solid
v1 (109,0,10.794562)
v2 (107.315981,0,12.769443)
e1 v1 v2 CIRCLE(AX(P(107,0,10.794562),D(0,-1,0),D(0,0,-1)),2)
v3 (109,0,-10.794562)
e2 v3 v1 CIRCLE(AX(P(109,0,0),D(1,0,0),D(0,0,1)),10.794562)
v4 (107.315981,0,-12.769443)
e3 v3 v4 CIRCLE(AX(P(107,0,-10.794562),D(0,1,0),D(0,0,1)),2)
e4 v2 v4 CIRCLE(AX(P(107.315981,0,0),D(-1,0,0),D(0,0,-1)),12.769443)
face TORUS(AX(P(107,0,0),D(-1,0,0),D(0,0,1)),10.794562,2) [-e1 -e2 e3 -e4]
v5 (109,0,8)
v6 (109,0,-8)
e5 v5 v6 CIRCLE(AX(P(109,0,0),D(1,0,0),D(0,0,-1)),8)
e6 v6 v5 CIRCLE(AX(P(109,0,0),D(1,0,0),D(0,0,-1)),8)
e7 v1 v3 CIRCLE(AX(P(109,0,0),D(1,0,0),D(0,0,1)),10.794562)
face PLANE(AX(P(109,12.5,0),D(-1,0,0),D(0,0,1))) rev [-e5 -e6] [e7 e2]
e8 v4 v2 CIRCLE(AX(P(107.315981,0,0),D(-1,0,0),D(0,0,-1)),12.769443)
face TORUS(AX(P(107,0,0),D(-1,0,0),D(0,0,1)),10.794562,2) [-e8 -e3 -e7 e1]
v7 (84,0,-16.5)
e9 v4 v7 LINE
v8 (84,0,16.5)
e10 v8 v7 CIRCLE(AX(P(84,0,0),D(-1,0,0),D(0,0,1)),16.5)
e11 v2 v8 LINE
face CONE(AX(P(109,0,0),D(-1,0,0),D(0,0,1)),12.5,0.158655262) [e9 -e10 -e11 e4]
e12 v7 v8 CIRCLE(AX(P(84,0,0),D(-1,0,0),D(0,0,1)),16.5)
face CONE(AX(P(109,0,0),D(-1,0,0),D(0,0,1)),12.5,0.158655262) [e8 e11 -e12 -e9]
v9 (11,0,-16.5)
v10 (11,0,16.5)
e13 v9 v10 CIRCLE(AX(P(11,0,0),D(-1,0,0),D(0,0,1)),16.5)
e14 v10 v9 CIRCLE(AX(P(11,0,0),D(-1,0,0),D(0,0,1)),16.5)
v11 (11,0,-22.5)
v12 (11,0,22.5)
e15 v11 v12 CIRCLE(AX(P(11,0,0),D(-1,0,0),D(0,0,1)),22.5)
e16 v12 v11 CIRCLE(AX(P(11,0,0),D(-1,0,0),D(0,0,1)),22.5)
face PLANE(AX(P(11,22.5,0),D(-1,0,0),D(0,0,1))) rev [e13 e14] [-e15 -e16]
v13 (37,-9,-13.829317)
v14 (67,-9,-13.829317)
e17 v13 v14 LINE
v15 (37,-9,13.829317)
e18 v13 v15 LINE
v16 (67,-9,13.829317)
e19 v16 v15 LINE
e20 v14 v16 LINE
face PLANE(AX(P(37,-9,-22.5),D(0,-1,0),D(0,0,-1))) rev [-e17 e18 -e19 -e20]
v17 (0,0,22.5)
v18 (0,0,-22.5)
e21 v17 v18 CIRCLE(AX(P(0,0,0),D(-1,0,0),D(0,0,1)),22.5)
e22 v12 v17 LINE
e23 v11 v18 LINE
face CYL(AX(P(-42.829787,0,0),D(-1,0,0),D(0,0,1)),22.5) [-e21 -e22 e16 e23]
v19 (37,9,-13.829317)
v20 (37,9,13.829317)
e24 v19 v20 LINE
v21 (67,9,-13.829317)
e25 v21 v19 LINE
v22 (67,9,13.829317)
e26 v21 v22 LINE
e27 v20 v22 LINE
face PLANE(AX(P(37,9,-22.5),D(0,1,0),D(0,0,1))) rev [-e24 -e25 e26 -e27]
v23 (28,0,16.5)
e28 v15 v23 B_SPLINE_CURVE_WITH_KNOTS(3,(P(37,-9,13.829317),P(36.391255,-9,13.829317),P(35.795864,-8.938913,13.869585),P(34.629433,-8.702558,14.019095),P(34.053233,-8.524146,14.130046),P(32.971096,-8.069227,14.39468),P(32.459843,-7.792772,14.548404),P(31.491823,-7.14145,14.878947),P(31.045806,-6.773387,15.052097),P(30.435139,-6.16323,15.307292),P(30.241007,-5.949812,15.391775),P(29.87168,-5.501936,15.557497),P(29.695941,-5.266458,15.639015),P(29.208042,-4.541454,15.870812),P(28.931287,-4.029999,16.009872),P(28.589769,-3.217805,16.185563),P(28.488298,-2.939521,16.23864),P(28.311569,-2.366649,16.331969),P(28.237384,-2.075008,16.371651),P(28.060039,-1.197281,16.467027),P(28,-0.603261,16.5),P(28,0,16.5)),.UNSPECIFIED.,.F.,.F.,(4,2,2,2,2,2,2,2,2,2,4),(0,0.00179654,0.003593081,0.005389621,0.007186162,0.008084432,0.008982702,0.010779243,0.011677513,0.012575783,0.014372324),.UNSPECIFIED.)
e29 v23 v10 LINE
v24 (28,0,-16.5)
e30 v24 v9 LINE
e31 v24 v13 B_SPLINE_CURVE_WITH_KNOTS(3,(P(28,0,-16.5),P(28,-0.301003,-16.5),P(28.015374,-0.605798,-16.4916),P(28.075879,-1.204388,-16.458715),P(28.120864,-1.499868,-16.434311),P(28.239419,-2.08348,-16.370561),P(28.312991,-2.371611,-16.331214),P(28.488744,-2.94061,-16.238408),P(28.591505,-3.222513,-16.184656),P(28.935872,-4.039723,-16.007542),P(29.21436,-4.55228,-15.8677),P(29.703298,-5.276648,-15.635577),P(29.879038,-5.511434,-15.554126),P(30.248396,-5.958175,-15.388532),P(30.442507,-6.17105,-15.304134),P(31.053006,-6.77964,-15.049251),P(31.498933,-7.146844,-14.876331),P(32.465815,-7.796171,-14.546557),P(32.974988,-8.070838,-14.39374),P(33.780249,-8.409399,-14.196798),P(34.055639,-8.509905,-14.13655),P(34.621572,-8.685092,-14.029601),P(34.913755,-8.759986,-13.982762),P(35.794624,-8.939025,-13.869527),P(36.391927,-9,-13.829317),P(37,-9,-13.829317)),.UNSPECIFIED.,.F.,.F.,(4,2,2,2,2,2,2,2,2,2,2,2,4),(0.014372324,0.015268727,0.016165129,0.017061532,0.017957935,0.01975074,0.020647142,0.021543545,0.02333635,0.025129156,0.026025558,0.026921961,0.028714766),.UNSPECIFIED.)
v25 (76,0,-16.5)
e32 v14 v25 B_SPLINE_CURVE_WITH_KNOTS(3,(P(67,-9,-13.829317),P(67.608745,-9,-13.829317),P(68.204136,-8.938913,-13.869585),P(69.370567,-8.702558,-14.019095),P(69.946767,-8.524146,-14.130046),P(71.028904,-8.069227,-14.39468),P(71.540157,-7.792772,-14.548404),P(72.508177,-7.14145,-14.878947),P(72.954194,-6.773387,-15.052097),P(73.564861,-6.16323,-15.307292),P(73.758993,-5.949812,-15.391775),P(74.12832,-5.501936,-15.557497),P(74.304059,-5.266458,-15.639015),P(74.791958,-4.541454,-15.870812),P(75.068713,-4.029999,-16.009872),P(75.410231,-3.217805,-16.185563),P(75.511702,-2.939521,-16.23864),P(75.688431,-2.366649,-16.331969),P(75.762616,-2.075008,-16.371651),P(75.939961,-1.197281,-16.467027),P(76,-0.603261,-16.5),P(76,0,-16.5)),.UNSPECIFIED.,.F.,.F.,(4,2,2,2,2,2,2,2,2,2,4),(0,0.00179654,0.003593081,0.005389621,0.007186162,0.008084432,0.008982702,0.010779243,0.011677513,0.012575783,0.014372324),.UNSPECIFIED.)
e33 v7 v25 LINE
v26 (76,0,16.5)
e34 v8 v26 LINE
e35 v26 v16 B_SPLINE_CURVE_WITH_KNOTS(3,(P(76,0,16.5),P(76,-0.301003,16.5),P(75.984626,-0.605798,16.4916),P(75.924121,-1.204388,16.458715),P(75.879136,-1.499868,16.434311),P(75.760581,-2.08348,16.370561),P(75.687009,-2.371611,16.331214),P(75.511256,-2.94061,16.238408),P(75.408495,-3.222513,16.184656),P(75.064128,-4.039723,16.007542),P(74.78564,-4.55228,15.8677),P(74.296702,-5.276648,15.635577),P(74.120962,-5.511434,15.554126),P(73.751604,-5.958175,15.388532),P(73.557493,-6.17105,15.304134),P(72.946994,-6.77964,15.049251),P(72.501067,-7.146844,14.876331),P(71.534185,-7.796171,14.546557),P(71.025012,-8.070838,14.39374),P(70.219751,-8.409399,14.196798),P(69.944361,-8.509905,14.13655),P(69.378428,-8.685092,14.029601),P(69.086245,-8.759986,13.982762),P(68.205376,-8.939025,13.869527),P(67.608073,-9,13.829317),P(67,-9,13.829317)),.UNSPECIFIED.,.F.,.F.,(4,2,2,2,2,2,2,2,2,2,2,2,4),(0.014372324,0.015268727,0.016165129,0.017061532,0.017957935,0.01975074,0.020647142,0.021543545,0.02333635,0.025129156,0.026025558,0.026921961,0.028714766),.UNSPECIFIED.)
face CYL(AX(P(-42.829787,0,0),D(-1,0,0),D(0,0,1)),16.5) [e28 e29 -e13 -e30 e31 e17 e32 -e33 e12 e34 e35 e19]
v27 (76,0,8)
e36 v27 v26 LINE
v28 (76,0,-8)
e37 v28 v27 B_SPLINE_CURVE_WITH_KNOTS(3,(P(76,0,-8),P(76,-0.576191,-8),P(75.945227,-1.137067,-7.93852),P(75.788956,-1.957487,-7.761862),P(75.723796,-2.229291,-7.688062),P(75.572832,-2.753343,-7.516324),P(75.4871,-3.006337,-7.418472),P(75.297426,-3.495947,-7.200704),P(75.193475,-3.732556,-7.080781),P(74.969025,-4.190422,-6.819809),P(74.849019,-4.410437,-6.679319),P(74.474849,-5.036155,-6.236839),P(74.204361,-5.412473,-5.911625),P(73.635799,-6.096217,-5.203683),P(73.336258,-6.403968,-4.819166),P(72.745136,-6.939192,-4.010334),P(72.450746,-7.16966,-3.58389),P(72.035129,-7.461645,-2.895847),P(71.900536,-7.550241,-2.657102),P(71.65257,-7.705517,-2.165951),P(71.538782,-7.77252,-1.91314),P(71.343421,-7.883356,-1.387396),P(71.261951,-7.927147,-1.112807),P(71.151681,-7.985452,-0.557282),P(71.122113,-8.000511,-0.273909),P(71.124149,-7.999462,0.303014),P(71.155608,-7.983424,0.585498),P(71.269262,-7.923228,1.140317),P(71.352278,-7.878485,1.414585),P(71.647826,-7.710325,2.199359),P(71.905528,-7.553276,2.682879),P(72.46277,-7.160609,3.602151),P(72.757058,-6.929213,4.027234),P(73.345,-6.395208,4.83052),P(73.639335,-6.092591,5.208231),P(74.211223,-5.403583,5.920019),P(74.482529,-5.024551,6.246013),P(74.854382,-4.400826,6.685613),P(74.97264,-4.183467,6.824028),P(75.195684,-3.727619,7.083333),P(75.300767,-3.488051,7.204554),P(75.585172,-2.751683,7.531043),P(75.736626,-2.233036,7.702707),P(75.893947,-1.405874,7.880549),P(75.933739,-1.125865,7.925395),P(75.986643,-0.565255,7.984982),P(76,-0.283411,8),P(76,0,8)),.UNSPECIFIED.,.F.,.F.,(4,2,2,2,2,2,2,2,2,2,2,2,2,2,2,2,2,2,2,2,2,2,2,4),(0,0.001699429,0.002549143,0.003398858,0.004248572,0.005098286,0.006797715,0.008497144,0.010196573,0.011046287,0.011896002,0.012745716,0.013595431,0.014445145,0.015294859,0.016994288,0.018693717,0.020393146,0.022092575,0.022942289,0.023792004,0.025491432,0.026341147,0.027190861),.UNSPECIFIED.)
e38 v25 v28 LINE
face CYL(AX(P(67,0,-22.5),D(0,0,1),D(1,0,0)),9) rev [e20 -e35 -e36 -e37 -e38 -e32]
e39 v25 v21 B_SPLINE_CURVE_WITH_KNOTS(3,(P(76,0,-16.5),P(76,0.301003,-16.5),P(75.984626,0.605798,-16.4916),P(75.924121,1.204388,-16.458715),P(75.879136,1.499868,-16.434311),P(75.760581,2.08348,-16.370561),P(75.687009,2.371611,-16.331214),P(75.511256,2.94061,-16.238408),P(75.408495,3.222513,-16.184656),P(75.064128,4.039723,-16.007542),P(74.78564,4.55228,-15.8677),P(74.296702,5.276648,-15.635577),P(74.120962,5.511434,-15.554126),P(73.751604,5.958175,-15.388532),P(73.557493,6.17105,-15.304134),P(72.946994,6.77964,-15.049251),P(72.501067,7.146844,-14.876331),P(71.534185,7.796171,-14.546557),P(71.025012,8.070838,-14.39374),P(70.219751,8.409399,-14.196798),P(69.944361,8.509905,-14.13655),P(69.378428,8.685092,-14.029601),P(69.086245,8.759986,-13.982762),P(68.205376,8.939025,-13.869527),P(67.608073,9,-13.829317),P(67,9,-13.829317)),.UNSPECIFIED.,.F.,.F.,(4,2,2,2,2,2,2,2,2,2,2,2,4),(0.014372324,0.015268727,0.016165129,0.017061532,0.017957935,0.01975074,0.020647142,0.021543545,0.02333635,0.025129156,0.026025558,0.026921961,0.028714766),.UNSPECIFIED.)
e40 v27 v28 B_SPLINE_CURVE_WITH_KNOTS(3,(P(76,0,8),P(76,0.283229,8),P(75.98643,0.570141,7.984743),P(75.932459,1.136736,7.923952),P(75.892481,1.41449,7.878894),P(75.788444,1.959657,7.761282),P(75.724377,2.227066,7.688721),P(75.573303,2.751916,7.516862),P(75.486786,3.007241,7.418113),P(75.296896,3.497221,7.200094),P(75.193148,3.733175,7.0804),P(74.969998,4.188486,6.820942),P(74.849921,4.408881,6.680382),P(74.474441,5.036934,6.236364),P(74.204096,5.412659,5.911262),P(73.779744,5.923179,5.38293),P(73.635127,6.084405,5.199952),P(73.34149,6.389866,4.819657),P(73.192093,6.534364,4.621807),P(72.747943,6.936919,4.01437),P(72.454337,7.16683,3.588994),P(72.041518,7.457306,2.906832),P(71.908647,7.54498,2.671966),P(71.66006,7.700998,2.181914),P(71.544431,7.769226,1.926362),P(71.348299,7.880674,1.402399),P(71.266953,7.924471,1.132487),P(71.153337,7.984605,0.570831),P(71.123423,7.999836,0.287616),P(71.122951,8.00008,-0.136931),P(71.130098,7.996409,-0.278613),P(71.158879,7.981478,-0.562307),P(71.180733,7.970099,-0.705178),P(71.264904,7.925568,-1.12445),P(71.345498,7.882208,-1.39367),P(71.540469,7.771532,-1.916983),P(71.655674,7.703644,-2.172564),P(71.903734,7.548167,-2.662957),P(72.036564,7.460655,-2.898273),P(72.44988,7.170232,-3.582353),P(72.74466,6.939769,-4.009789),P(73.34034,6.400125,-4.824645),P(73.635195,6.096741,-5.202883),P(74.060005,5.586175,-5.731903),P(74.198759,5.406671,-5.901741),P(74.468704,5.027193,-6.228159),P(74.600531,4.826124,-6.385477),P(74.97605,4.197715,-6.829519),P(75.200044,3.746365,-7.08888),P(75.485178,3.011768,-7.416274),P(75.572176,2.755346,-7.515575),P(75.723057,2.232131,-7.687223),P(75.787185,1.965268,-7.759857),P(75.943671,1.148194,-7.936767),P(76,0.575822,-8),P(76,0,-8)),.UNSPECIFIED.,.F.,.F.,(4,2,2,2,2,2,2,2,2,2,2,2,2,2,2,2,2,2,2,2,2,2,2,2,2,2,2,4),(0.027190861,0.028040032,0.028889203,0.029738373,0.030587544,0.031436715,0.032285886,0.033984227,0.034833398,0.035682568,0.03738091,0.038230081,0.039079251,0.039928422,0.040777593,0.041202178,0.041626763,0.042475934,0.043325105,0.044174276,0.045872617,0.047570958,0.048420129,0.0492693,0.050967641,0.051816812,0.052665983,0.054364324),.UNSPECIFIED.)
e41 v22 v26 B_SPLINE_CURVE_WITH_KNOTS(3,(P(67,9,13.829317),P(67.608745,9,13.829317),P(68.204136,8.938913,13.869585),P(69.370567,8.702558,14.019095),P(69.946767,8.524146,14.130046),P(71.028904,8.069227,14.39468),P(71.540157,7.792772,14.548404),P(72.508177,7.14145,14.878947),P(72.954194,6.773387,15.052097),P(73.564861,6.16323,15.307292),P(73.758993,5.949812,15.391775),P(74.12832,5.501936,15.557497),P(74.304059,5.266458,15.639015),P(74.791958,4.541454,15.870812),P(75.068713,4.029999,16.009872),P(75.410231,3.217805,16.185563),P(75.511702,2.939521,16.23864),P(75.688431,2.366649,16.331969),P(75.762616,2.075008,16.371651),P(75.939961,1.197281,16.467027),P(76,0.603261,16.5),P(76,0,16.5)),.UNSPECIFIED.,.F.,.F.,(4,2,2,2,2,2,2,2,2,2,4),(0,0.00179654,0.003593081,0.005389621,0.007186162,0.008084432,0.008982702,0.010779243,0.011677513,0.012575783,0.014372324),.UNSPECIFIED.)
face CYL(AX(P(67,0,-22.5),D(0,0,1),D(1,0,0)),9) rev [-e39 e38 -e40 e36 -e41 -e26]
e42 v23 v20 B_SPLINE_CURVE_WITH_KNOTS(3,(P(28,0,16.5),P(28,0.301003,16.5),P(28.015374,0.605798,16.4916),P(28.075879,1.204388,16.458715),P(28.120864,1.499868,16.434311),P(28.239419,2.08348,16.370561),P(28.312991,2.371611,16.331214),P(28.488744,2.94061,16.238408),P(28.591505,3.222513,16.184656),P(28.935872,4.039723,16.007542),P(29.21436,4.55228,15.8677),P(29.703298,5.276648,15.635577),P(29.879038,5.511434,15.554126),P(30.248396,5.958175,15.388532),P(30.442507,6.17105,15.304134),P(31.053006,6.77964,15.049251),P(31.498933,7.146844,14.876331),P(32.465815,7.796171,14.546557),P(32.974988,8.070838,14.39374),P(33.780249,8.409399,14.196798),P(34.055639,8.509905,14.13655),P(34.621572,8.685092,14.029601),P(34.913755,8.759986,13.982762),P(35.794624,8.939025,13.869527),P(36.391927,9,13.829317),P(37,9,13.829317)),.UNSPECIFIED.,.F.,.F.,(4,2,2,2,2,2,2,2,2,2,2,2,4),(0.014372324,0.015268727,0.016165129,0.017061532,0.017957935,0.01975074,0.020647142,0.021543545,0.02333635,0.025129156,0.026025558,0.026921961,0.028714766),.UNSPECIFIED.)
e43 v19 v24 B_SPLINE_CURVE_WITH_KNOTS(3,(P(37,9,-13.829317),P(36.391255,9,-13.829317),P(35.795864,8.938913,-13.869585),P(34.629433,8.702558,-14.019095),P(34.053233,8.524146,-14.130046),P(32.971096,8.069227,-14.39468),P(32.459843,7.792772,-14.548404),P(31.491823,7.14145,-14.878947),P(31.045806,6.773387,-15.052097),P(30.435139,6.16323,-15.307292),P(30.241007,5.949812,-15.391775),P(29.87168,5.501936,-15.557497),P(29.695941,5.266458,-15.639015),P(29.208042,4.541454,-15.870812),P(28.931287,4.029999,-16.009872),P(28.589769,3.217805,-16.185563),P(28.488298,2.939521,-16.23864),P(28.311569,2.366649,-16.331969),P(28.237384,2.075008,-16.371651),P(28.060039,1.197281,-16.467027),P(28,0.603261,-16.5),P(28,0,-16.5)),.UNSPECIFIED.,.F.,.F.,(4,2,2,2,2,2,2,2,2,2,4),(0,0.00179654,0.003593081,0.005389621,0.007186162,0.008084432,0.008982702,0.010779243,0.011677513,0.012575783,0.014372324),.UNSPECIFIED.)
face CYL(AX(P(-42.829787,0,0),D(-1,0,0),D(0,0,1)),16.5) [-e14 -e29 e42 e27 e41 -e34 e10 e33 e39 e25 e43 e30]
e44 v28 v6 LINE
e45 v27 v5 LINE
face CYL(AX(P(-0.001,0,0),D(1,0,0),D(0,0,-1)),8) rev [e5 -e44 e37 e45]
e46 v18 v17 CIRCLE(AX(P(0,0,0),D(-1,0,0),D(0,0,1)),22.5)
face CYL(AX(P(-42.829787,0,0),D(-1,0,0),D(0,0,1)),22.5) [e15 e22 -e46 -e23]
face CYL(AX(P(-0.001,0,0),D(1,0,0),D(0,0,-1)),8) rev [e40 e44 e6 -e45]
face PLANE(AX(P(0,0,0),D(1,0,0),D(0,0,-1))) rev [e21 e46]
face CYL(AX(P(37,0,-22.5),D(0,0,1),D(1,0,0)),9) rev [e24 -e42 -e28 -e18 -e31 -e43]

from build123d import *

# Parameters (mm, degrees)
SIDE_WINDOW_CUT_DEPTH      = 114.549548656
SIDE_WINDOW_CUT_DEPTH_BACK = 114.549548656
EDGE_FILLET_R2_R           = 2
BORE_16_REACH              = 115.55
BORE_16_END_RADIUS         = 9
BORE_SKETCH_16_R           = 8


with BuildPart() as part:
    # Holder Profile Sketch → Holder Body Revolve (revolve)
    with BuildSketch(Plane.XY, mode=Mode.PRIVATE) as holder_body_revolve_sk:
        Polygon((0, 0), (0, 22.5), (11, 22.5), (11, 16.5), (84, 16.5), (109, 12.5), (109, 0), align=None)
    revolve(holder_body_revolve_sk.sketch.rotate(Axis((-42.829787234, 0, 0), (1, 0, 0)), 90), axis=Axis((-42.829787234, 0, 0), (1, 0, 0)))

    # Side Window Sketch → Side Window Cut (cut, two sides: drawn at the far end of the back side and taken through both)
    with BuildSketch(Plane.XY.offset(-SIDE_WINDOW_CUT_DEPTH_BACK)):
        with BuildLine():
            Line((37, 9), (67, 9))
            ThreePointArc((67, 9), (76, 0), (67, -9))
            Line((67, -9), (37, -9))
            ThreePointArc((37, -9), (28, 0), (37, 9))
        make_face()
    extrude(amount=SIDE_WINDOW_CUT_DEPTH + SIDE_WINDOW_CUT_DEPTH_BACK, mode=Mode.SUBTRACT)

    # Edge Fillet R2
    edge_fillet_r2_edges = [part.edges().sort_by_distance(p)[0] for p in [
        (109, 0, -12.5),
    ]]
    fillet(edge_fillet_r2_edges, radius=EDGE_FILLET_R2_R)

    # Bore Ø16: up to this cylinder (the profile starts outside it)
    bore_16_end = Plane(origin=(67, 0, 0), z_dir=(0, 0, 1)) * Cylinder(BORE_16_END_RADIUS, 250.1, mode=Mode.PRIVATE)
    # Bore Sketch Ø16 → Bore Ø16 (cut, up to the surface)
    with BuildSketch(Plane(origin=(109, 0, 0), x_dir=(0, 0, -1), z_dir=(1, 0, 0)), mode=Mode.PRIVATE) as bore_16_sk1:
        Circle(BORE_SKETCH_16_R)
    bore_16_tool1 = extrude(bore_16_sk1.sketch, amount=-BORE_16_REACH, mode=Mode.PRIVATE) - bore_16_end
    add(bore_16_tool1.solids().sort_by_distance((109, 0, 0))[0], mode=Mode.SUBTRACT)


solid = part.part
